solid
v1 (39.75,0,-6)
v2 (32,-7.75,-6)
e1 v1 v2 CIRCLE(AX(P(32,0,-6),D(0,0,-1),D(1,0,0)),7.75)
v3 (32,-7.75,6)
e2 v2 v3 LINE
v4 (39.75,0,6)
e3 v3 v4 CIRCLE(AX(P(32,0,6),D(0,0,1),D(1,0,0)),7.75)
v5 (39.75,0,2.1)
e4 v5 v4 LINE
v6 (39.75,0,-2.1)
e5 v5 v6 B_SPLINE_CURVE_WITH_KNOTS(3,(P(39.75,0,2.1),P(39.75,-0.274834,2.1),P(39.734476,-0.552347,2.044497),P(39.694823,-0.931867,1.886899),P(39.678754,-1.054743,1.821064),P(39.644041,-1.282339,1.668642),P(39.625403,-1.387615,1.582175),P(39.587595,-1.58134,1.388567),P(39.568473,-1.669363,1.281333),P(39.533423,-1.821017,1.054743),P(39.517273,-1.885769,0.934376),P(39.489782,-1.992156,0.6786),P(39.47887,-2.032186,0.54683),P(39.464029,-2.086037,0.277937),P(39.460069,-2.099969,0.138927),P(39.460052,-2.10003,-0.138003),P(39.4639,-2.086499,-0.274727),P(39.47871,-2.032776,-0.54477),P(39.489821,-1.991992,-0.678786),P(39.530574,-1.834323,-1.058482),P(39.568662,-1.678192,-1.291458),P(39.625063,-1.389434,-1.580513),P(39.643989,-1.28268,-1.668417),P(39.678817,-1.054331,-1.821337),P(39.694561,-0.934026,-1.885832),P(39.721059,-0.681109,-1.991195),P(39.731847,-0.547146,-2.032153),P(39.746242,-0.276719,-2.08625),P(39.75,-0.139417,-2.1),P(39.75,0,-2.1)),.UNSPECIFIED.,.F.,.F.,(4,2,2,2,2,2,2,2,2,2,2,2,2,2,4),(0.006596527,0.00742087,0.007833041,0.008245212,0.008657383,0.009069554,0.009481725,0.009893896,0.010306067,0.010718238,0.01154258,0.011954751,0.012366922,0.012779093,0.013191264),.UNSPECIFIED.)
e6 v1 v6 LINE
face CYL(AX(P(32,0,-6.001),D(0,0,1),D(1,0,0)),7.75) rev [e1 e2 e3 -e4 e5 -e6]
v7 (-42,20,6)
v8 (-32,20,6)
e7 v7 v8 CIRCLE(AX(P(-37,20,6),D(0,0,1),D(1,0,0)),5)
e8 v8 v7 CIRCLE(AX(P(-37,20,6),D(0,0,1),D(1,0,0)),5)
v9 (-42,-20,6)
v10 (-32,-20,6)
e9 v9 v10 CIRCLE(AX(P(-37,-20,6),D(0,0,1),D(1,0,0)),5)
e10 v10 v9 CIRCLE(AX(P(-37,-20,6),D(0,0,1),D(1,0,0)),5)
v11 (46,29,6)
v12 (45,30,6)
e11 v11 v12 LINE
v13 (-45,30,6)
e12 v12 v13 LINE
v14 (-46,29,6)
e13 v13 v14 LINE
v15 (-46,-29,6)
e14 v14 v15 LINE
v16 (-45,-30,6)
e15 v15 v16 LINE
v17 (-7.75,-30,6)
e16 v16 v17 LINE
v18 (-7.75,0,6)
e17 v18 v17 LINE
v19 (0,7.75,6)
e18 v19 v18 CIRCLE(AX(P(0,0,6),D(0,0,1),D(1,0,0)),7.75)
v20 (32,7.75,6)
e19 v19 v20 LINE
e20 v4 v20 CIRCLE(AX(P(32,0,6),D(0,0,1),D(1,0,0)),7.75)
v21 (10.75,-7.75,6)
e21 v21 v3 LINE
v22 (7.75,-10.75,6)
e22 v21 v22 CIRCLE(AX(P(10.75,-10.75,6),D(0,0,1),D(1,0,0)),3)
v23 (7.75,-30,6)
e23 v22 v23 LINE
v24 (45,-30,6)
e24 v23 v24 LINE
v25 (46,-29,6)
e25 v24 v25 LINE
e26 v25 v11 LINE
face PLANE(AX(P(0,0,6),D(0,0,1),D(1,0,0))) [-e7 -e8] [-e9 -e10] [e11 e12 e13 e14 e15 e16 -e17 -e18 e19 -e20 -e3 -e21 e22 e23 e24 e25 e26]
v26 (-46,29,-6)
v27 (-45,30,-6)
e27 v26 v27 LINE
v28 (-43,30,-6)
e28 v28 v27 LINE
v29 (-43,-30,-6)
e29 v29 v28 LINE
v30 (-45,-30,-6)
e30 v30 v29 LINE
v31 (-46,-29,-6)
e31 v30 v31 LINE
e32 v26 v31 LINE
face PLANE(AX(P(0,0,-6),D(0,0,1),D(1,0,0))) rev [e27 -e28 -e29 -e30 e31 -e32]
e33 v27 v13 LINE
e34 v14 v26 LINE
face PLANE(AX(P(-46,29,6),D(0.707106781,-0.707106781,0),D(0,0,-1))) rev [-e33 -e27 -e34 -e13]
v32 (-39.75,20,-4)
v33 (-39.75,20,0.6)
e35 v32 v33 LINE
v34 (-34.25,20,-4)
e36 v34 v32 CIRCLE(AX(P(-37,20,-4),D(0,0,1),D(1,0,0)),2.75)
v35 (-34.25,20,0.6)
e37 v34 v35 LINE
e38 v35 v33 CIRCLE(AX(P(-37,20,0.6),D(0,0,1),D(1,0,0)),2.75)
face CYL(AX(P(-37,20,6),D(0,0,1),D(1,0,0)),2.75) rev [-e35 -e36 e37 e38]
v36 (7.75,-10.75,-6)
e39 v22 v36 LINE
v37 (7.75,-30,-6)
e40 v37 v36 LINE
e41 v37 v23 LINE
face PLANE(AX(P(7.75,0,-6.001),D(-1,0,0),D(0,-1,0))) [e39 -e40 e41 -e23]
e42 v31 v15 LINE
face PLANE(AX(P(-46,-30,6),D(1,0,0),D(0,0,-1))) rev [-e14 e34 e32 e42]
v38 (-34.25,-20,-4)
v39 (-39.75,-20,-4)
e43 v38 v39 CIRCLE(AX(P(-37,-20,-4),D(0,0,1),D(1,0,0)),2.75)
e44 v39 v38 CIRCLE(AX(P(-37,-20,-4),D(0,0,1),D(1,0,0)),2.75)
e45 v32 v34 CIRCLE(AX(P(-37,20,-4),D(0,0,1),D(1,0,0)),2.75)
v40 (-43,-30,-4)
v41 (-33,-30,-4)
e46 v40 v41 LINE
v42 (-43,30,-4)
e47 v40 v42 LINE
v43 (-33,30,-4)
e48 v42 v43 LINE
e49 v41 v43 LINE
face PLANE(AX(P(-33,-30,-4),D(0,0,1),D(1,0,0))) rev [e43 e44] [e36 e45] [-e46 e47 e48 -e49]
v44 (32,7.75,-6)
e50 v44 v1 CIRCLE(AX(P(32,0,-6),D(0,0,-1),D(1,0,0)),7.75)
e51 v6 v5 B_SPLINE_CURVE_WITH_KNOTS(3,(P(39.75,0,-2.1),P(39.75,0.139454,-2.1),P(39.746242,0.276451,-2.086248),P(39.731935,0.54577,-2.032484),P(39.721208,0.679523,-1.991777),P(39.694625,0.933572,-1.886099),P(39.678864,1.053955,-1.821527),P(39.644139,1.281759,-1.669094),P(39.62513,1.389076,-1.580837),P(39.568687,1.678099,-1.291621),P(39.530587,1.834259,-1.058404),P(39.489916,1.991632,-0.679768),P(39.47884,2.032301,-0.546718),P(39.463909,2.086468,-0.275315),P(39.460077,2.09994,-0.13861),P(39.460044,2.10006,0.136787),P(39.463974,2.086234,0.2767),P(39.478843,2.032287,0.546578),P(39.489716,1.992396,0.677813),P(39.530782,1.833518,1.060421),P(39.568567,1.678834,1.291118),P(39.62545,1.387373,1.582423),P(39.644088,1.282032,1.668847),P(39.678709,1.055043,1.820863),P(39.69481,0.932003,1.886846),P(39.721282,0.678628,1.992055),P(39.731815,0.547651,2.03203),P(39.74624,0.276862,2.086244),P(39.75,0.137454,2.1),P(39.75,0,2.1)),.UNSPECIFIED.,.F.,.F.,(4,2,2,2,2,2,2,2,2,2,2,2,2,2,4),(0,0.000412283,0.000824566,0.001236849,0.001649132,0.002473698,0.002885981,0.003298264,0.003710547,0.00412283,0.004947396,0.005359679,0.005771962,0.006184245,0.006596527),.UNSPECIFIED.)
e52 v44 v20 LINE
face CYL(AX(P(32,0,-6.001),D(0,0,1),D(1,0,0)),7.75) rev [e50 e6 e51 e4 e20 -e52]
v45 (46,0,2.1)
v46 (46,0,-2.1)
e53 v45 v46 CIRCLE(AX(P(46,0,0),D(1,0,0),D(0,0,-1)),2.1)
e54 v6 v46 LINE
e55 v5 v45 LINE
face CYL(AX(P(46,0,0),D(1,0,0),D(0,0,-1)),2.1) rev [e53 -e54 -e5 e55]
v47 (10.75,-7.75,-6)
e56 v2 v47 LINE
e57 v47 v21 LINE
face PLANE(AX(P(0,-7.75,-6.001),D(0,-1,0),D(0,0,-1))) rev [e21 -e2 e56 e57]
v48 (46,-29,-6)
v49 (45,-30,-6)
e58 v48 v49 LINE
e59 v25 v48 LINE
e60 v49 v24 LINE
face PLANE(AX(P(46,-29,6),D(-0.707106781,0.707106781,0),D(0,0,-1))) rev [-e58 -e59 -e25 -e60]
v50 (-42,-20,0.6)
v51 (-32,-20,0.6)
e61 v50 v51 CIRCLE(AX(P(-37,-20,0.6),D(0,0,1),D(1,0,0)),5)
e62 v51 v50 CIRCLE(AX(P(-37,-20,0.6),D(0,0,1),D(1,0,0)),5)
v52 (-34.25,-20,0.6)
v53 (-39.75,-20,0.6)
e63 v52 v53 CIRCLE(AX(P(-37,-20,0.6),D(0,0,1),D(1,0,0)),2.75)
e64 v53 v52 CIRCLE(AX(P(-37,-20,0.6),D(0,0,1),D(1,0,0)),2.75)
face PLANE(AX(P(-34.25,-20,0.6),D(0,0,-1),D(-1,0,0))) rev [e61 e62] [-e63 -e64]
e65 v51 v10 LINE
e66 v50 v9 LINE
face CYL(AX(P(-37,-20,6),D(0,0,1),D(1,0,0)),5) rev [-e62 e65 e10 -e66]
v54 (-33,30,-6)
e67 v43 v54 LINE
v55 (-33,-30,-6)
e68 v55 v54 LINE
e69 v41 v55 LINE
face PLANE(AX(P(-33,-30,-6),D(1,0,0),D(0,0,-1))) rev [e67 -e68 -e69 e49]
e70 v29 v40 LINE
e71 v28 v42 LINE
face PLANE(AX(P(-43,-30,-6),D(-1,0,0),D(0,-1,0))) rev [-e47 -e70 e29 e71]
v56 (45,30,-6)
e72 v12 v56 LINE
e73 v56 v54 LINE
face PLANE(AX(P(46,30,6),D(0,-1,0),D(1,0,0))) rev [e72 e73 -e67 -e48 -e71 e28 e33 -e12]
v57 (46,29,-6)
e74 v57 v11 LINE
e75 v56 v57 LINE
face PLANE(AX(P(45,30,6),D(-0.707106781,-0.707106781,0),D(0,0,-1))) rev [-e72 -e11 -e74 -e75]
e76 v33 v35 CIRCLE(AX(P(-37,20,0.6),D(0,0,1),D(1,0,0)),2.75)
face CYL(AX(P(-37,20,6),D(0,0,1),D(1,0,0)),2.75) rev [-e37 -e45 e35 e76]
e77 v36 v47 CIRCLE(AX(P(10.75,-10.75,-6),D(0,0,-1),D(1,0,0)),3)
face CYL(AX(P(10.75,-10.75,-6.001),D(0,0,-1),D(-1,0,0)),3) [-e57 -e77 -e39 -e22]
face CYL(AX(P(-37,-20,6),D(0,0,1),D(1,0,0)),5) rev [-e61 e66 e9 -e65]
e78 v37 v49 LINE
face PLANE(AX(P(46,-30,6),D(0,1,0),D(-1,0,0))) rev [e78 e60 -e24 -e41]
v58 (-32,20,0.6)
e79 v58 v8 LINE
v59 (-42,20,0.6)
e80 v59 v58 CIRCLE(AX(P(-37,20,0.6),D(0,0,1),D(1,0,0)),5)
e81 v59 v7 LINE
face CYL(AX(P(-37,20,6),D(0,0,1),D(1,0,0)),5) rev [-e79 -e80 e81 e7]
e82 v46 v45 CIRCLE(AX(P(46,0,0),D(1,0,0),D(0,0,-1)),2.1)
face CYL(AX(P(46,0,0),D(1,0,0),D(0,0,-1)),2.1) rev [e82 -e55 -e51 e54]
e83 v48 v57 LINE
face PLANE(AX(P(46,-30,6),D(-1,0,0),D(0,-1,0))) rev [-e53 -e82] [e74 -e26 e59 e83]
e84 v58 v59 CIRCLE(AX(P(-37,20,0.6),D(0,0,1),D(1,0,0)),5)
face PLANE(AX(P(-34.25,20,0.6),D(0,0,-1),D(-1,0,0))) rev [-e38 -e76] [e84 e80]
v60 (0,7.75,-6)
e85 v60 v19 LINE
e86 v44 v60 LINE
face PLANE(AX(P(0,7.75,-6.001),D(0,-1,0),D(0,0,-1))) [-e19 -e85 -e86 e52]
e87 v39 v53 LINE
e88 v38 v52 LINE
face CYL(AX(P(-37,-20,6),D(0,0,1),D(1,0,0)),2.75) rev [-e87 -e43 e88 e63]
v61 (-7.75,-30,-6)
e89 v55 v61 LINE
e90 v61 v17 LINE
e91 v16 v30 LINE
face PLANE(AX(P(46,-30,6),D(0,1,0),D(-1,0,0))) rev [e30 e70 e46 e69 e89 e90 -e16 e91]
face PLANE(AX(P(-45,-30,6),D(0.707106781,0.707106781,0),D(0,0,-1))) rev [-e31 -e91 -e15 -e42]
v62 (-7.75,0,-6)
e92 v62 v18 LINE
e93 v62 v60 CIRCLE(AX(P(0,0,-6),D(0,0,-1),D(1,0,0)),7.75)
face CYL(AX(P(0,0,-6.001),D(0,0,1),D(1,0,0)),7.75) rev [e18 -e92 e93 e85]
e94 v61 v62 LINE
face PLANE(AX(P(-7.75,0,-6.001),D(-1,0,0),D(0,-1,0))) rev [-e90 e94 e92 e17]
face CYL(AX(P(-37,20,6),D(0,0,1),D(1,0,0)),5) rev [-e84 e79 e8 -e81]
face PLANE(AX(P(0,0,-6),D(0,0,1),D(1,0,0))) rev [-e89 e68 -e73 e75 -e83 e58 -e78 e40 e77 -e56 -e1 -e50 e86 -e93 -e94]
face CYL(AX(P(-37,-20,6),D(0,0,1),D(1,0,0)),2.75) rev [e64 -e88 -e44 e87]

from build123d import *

# Parameters (mm, degrees)
SKETCH_1_W                     = 92
SKETCH_1_H                     = 60
EXTRUDE_1_DEPTH                = 6
CHAMFER_1_SIZE                 = 1
SKETCH_2_W                     = 10
SKETCH_2_H                     = 2
CUT_EXTRUDE_1_DEPTH            = 76.841940903
CUT_EXTRUDE_3_REACH            = 58.214
FILLET_1_R                     = 3
HOLE_WIZARD_M5_1_REACH         = 98.954
HOLE_WIZARD_M5_1_BORE_R        = 2.1
HOLE_WIZARD_M5_1_2_D           = 5.5
HOLE_WIZARD_M5_1_2_CBORE_D     = 10
HOLE_WIZARD_M5_1_2_CBORE_DEPTH = 5.4


with BuildPart() as part:
    # 草图1 → 凸台-拉伸1 (new, symmetric)
    with BuildSketch(Plane.XY):
        Rectangle(SKETCH_1_W, SKETCH_1_H)
    extrude(amount=EXTRUDE_1_DEPTH, both=True)

    # 倒角1
    chamfer_1_edges = [part.edges().sort_by_distance(p)[0] for p in [
        (-46, 30, 0),
        (46, 30, 0),
        (46, -30, 0),
        (-46, -30, 0),
    ]]
    chamfer(chamfer_1_edges, length=CHAMFER_1_SIZE)

    # 草图2 → 切除-拉伸1 (cut, through all)
    with BuildSketch(Plane(origin=(0, 30, 0), x_dir=(1, 0, 0), z_dir=(0, 1, 0))):
        with Locations((-38, 5)):
            Rectangle(SKETCH_2_W, SKETCH_2_H)
    extrude(amount=-CUT_EXTRUDE_1_DEPTH, mode=Mode.SUBTRACT)

    # 草图3 → 切除-拉伸3 (cut, up to next)
    with BuildSketch(Plane.XY.offset(6), mode=Mode.PRIVATE) as cut_extrude_3_sk1:
        with BuildLine():
            Line((7.75, 0), (7.75, -35))
            ThreePointArc((7.75, -35), (0, -42.75), (-7.75, -35))
            Line((-7.75, -35), (-7.75, 0))
            ThreePointArc((-7.75, 0), (0, 7.75), (7.75, 0))
        make_face()
    cut_extrude_3_tool1 = extrude(cut_extrude_3_sk1.sketch, amount=-CUT_EXTRUDE_3_REACH, mode=Mode.PRIVATE) & part.part
    # 草图3 → 切除-拉伸3 (cut, up to next)
    with BuildSketch(Plane.XY.offset(6), mode=Mode.PRIVATE) as cut_extrude_3_sk2:
        with BuildLine():
            Line((0, 7.75), (32, 7.75))
            ThreePointArc((32, 7.75), (39.75, 0), (32, -7.75))
            Line((32, -7.75), (0, -7.75))
            ThreePointArc((0, -7.75), (-7.75, 0), (0, 7.75))
        make_face()
    cut_extrude_3_tool2 = extrude(cut_extrude_3_sk2.sketch, amount=-CUT_EXTRUDE_3_REACH, mode=Mode.PRIVATE) & part.part
    add(cut_extrude_3_tool1.solids().sort_by_distance((0, -17.5, 6))[0], mode=Mode.SUBTRACT)
    add(cut_extrude_3_tool2.solids().sort_by_distance((16, 0, 6))[0], mode=Mode.SUBTRACT)

    # 圆角1
    fillet_1_edges = [part.edges().sort_by_distance(p)[0] for p in [
        (7.75, -7.75, 0),
    ]]
    fillet(fillet_1_edges, radius=FILLET_1_R)

    # Hole Wizard M5 _1 bore → Hole Wizard M5 _1 (cut, up to next)
    with BuildSketch(Plane(origin=(46, 0, 0), x_dir=(0, 0, -1), z_dir=(1, 0, 0)), mode=Mode.PRIVATE) as hole_wizard_m5_1_sk1:
        Circle(HOLE_WIZARD_M5_1_BORE_R)
    hole_wizard_m5_1_tool1 = extrude(hole_wizard_m5_1_sk1.sketch, amount=-HOLE_WIZARD_M5_1_REACH, mode=Mode.PRIVATE) & part.part
    add(hole_wizard_m5_1_tool1.solids().sort_by_distance((46, 0, 0))[0], mode=Mode.SUBTRACT)

    # Hole Wizard M5 _1 2 (through all)
    with Locations(Plane.XY.offset(6)):
        with Locations((-37, -20), (-37, 20)):
            CounterBoreHole(HOLE_WIZARD_M5_1_2_D / 2, HOLE_WIZARD_M5_1_2_CBORE_D / 2, HOLE_WIZARD_M5_1_2_CBORE_DEPTH)


solid = part.part
